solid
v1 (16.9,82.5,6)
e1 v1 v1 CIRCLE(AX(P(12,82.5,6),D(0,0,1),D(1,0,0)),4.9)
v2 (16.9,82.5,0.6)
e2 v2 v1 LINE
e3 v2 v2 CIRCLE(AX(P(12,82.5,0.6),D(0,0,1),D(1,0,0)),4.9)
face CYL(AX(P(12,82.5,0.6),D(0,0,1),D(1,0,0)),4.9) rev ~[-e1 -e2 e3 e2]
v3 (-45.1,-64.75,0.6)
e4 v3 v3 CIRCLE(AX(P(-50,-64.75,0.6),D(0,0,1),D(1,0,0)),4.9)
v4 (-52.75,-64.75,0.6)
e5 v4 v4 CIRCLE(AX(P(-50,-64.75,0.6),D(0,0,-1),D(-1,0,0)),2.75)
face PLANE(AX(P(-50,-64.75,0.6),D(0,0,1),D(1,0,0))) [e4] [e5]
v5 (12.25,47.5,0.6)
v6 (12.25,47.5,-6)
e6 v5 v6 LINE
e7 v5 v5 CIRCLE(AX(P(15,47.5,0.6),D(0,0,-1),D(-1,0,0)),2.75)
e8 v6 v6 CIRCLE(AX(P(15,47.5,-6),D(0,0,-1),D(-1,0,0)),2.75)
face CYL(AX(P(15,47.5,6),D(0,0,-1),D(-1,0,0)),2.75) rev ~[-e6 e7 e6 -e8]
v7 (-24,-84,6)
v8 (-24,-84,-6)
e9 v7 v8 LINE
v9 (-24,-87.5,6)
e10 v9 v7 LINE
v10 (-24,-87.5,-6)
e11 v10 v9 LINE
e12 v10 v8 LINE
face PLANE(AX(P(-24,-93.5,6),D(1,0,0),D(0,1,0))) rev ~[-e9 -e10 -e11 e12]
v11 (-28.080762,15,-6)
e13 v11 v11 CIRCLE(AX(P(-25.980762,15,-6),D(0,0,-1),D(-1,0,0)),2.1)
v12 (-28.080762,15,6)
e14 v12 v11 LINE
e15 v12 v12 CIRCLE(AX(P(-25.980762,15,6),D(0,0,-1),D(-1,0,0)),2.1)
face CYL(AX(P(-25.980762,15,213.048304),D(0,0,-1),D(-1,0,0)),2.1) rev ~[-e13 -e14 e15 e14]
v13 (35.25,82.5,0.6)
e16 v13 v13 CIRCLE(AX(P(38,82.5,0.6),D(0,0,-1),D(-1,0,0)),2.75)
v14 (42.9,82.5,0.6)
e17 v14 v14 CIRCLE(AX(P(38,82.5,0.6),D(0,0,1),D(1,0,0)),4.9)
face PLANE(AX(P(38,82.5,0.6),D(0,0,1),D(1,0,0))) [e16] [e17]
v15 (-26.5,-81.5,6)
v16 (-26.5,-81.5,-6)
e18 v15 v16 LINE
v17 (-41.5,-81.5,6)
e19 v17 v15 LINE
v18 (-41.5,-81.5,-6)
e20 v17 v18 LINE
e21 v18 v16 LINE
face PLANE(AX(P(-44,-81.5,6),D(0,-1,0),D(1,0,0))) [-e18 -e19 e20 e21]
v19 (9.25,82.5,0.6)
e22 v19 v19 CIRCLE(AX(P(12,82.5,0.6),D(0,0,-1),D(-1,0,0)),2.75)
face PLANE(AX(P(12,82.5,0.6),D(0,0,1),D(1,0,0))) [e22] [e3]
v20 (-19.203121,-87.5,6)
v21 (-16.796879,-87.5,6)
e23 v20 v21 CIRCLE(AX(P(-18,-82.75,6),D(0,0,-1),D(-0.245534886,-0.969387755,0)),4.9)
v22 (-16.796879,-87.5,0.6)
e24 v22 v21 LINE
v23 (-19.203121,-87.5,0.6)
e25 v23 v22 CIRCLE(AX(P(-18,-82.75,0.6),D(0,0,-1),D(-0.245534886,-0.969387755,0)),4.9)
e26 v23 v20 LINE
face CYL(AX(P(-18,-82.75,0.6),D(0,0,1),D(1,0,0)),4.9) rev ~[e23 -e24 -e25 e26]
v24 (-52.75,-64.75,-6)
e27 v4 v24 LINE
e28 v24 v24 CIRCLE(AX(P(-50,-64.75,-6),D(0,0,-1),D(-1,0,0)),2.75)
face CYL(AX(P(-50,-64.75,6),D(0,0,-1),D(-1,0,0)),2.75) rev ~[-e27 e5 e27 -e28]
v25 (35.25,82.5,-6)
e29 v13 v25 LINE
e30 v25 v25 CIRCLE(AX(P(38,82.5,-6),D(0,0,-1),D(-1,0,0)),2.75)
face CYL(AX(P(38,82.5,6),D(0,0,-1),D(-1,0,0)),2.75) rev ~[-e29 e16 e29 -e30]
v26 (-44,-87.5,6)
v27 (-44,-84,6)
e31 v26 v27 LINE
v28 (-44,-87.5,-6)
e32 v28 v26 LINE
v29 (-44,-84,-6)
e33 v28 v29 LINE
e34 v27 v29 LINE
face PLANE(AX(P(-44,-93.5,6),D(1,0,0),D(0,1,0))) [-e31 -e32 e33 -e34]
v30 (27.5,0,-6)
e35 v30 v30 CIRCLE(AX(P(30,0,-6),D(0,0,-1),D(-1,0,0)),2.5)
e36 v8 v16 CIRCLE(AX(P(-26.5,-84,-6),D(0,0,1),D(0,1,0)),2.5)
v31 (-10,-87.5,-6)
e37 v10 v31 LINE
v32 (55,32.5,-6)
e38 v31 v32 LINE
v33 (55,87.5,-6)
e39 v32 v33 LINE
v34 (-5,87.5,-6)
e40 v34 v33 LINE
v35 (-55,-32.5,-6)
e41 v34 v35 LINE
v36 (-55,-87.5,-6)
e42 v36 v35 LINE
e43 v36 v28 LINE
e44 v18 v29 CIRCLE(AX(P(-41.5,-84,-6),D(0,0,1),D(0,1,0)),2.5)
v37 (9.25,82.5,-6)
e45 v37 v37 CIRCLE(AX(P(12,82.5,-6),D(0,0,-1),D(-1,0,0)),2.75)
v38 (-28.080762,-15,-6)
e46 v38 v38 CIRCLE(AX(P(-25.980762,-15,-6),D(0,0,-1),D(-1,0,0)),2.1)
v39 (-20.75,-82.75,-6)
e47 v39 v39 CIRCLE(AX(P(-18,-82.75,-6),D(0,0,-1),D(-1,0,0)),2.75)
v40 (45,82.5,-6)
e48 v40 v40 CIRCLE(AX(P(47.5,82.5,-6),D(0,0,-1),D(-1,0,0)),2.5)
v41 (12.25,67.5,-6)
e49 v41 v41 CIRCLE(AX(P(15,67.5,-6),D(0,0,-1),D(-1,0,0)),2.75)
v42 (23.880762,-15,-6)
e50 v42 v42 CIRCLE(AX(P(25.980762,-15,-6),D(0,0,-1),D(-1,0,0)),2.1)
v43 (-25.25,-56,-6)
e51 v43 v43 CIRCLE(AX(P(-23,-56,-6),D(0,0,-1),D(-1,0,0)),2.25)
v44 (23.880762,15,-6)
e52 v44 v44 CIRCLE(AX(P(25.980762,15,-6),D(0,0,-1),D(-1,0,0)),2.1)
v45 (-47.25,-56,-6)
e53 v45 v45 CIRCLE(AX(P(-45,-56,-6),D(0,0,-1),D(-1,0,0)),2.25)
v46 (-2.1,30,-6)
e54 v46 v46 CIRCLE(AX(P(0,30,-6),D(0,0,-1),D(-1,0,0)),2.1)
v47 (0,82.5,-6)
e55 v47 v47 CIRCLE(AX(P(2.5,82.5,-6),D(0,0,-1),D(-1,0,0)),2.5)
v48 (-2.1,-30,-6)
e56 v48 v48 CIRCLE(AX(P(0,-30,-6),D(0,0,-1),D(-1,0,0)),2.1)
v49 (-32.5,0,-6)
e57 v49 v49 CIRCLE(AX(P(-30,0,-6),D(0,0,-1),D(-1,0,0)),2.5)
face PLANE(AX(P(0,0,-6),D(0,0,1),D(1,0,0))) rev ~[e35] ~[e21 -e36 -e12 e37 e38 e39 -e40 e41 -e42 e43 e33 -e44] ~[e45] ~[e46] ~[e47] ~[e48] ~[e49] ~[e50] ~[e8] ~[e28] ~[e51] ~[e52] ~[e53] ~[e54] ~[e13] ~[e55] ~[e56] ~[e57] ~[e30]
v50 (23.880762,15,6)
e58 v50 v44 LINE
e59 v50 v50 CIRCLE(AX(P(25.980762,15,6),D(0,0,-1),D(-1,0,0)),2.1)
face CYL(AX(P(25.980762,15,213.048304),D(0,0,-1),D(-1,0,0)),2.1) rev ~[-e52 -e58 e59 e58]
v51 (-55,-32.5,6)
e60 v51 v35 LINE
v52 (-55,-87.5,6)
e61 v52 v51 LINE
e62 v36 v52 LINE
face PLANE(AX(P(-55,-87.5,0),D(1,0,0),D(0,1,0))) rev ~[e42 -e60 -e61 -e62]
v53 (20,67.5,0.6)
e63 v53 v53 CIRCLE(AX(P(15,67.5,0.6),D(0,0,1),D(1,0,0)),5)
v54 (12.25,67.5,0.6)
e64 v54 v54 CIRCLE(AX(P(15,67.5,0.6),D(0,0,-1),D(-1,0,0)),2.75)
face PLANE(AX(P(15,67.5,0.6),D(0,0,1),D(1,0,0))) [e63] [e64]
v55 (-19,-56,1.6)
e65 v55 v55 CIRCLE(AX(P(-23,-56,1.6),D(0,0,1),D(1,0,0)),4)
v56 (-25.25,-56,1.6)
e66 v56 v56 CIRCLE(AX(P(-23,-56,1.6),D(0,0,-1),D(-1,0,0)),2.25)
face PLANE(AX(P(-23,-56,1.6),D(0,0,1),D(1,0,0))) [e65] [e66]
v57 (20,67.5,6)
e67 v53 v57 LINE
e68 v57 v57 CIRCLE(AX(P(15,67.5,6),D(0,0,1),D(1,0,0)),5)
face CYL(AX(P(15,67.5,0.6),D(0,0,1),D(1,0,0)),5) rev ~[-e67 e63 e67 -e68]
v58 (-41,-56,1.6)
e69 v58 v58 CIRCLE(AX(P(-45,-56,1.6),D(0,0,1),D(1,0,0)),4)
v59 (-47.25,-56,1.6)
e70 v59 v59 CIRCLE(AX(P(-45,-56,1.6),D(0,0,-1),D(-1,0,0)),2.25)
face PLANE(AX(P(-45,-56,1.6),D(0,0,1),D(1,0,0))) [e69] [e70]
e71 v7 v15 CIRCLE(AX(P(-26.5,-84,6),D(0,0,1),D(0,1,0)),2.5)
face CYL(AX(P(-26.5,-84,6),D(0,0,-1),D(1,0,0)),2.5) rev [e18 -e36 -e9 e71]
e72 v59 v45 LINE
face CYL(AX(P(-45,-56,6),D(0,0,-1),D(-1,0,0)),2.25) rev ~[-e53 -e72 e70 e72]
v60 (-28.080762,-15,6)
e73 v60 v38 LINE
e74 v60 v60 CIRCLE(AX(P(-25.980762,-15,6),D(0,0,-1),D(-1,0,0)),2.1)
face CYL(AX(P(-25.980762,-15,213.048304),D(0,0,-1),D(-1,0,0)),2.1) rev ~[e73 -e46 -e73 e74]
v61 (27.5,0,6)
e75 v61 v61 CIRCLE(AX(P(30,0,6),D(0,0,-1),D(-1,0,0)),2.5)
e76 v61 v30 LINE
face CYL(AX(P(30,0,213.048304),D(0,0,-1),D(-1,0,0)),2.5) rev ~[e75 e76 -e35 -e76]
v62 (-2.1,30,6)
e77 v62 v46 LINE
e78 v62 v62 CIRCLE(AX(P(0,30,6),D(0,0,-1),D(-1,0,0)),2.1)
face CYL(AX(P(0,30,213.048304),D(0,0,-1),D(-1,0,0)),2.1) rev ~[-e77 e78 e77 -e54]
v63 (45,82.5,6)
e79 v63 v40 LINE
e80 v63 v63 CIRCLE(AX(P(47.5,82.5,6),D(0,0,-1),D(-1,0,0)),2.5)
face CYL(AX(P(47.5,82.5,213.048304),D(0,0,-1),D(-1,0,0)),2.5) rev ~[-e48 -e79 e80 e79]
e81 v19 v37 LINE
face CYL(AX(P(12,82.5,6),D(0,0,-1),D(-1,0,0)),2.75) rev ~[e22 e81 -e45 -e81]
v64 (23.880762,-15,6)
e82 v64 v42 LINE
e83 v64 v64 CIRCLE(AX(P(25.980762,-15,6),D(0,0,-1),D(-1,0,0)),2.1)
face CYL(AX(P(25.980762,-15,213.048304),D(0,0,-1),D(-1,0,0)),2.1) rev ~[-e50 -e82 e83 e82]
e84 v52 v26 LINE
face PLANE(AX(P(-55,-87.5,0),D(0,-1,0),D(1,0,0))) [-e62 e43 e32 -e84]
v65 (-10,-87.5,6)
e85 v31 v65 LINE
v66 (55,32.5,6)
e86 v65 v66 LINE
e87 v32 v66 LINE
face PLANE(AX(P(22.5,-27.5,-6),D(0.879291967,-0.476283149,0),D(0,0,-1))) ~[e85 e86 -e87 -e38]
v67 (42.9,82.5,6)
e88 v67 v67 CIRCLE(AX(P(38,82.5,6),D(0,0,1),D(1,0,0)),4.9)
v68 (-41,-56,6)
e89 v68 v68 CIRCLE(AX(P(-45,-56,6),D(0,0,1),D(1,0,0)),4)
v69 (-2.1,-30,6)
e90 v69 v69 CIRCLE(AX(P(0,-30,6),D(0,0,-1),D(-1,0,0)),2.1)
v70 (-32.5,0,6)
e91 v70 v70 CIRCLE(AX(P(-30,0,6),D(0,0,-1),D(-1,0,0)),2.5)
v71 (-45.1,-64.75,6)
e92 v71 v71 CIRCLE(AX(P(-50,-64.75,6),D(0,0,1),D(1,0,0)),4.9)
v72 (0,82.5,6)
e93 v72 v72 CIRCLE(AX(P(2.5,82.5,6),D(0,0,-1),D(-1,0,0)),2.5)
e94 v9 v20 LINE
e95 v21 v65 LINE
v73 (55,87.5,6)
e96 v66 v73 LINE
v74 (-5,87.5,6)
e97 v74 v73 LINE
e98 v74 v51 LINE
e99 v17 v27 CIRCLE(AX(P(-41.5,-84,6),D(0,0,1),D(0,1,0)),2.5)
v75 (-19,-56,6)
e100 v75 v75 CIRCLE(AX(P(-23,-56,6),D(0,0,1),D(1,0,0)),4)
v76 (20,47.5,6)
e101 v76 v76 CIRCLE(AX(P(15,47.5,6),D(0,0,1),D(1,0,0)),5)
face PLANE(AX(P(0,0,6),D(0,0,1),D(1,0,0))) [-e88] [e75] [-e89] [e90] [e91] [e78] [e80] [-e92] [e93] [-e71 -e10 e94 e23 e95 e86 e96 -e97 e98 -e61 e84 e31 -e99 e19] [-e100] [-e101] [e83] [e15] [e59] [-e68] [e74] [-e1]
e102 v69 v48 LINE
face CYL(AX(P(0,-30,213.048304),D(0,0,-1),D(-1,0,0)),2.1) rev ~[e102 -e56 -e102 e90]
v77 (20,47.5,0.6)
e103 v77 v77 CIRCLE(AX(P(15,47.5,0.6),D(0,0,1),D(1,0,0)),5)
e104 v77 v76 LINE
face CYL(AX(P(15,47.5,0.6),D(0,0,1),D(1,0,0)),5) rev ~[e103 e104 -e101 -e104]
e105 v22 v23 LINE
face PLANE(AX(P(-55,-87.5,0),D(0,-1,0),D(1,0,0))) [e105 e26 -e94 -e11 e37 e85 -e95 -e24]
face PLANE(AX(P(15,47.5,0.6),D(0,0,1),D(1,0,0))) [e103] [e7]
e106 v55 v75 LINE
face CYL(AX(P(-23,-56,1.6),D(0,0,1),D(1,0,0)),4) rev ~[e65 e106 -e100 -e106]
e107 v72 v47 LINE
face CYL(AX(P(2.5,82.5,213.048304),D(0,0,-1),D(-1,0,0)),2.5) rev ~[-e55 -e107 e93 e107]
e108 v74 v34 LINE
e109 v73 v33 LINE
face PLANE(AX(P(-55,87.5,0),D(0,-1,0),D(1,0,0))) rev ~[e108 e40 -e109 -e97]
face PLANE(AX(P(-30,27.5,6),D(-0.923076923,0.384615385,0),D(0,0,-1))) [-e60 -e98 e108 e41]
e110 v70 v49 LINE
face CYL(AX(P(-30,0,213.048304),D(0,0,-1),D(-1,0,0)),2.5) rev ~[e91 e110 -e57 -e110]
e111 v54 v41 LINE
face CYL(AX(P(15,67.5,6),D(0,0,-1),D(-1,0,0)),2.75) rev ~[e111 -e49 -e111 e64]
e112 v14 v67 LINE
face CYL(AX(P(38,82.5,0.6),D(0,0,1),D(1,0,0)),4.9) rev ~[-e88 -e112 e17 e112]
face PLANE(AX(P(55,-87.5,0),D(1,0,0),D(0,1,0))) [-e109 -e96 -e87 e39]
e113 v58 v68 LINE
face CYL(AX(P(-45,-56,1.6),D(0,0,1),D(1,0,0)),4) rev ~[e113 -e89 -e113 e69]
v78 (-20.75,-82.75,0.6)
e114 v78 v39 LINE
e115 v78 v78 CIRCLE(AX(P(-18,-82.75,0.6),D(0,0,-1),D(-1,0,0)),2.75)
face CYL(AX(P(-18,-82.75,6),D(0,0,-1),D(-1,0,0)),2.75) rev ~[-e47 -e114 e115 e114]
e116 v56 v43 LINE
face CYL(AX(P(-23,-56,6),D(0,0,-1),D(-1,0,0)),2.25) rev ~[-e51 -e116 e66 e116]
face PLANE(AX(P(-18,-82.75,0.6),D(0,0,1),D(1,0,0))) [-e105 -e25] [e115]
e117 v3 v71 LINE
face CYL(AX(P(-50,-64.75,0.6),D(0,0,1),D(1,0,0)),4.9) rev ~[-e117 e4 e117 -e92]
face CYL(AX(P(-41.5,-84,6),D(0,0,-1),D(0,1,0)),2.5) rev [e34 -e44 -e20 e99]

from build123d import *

# Parameters (mm, degrees)
SKETCH_1_W                   = 110
SKETCH_1_H                   = 175
EXTRUDE_1_DEPTH              = 6
CHAMFER_1_SIZE               = 50
CHAMFER_1_SIZE2              = 120
CHAMFER_2_SIZE               = 65
CHAMFER_2_SIZE2              = 120
HOLE_WIZARD_M5_1_D           = 5
HOLE_WIZARD_M5_1_2_D         = 4.2
F_5_0MM_1_D                  = 5
HOLE_WIZARD_M5_3_D           = 5.5
HOLE_WIZARD_M5_3_CBORE_D     = 9.8
HOLE_WIZARD_M5_3_CBORE_DEPTH = 5.4
HOLE_WIZARD_M5_4_D           = 5.5
HOLE_WIZARD_M5_4_CBORE_D     = 10
HOLE_WIZARD_M5_4_CBORE_DEPTH = 5.4
HOLE_WIZARD_M4_1_D           = 4.5
HOLE_WIZARD_M4_1_CBORE_D     = 8
HOLE_WIZARD_M4_1_CBORE_DEPTH = 4.4
HOLE_WIZARD_M5_6_D           = 5.5
HOLE_WIZARD_M5_6_CBORE_D     = 9.8
HOLE_WIZARD_M5_6_CBORE_DEPTH = 5.4
SKETCH_16_W                  = 20
SKETCH_16_H                  = 12
CUT_EXTRUDE_1_DEPTH          = 105.04446165
FILLET_1_R                   = 2.5


with BuildPart() as part:
    # 草图1 → 凸台-拉伸1 (new, symmetric)
    with BuildSketch(Plane.XY):
        Rectangle(SKETCH_1_W, SKETCH_1_H)
    extrude(amount=EXTRUDE_1_DEPTH, both=True)

    # 倒角1
    chamfer_1_edges = [part.edges().sort_by_distance(p)[0] for p in [
        (-55, 87.5, 0),
    ]]
    chamfer_1_side = [part.faces().sort_by_distance(p)[0] for p in [
        (0, 87.5, 0),
    ]]
    chamfer(chamfer_1_edges, length=CHAMFER_1_SIZE, length2=CHAMFER_1_SIZE2, reference=chamfer_1_side[0])

    # 倒角2
    chamfer_2_edges = [part.edges().sort_by_distance(p)[0] for p in [
        (55, -87.5, 0),
    ]]
    chamfer_2_side = [part.faces().sort_by_distance(p)[0] for p in [
        (0, -87.5, 0),
    ]]
    chamfer(chamfer_2_edges, length=CHAMFER_2_SIZE, length2=CHAMFER_2_SIZE2, reference=chamfer_2_side[0])

    # Hole Wizard M5 _1 (through all)
    with Locations(Plane.XY.offset(6)):
        with Locations((47.5, 82.5), (2.5, 82.5)):
            Hole(HOLE_WIZARD_M5_1_D / 2)

    # Hole Wizard M5 _1 2 (through all)
    with Locations(Plane.XY.offset(6)):
        with Locations((0, 30), (25.980762114, 15), (25.980762114, -15), (0, -30), (-25.980762114, -15), (-25.980762114, 15)):
            Hole(HOLE_WIZARD_M5_1_2_D / 2)

    # Ø5.0mm 暗销孔1 (through all)
    with Locations(Plane.XY.offset(6)):
        with Locations((30, 0), (-30, 0)):
            Hole(F_5_0MM_1_D / 2)

    # M5 六角凹头螺钉的柱形沉头孔3 (through all)
    with Locations(Plane.XY.offset(6)):
        with Locations((38, 82.5), (12, 82.5)):
            CounterBoreHole(HOLE_WIZARD_M5_3_D / 2, HOLE_WIZARD_M5_3_CBORE_D / 2, HOLE_WIZARD_M5_3_CBORE_DEPTH)

    # M5 六角凹头螺钉的柱形沉头孔4 (through all)
    with Locations(Plane.XY.offset(6)):
        with Locations((15, 67.5), (15, 47.5)):
            CounterBoreHole(HOLE_WIZARD_M5_4_D / 2, HOLE_WIZARD_M5_4_CBORE_D / 2, HOLE_WIZARD_M5_4_CBORE_DEPTH)

    # M4 六角凹头螺钉的柱形沉头孔1 (through all)
    with Locations(Plane.XY.offset(6)):
        with Locations((-45, -56), (-23, -56)):
            CounterBoreHole(HOLE_WIZARD_M4_1_D / 2, HOLE_WIZARD_M4_1_CBORE_D / 2, HOLE_WIZARD_M4_1_CBORE_DEPTH)

    # M5 六角凹头螺钉的柱形沉头孔6 (through all)
    with Locations(Plane.XY.offset(6)):
        with Locations((-50, -64.75), (-18, -82.75)):
            CounterBoreHole(HOLE_WIZARD_M5_6_D / 2, HOLE_WIZARD_M5_6_CBORE_D / 2, HOLE_WIZARD_M5_6_CBORE_DEPTH)

    # 草图16 → 切除-拉伸1 (cut, through all)
    with BuildSketch(Plane.XY.offset(6)):
        with Locations((-34, -87.5)):
            Rectangle(SKETCH_16_W, SKETCH_16_H)
    extrude(amount=-CUT_EXTRUDE_1_DEPTH, mode=Mode.SUBTRACT)

    # 圆角1
    fillet_1_edges = [part.edges().sort_by_distance(p)[0] for p in [
        (-24, -81.5, 0),
        (-44, -81.5, 0),
    ]]
    fillet(fillet_1_edges, radius=FILLET_1_R)


solid = part.part
